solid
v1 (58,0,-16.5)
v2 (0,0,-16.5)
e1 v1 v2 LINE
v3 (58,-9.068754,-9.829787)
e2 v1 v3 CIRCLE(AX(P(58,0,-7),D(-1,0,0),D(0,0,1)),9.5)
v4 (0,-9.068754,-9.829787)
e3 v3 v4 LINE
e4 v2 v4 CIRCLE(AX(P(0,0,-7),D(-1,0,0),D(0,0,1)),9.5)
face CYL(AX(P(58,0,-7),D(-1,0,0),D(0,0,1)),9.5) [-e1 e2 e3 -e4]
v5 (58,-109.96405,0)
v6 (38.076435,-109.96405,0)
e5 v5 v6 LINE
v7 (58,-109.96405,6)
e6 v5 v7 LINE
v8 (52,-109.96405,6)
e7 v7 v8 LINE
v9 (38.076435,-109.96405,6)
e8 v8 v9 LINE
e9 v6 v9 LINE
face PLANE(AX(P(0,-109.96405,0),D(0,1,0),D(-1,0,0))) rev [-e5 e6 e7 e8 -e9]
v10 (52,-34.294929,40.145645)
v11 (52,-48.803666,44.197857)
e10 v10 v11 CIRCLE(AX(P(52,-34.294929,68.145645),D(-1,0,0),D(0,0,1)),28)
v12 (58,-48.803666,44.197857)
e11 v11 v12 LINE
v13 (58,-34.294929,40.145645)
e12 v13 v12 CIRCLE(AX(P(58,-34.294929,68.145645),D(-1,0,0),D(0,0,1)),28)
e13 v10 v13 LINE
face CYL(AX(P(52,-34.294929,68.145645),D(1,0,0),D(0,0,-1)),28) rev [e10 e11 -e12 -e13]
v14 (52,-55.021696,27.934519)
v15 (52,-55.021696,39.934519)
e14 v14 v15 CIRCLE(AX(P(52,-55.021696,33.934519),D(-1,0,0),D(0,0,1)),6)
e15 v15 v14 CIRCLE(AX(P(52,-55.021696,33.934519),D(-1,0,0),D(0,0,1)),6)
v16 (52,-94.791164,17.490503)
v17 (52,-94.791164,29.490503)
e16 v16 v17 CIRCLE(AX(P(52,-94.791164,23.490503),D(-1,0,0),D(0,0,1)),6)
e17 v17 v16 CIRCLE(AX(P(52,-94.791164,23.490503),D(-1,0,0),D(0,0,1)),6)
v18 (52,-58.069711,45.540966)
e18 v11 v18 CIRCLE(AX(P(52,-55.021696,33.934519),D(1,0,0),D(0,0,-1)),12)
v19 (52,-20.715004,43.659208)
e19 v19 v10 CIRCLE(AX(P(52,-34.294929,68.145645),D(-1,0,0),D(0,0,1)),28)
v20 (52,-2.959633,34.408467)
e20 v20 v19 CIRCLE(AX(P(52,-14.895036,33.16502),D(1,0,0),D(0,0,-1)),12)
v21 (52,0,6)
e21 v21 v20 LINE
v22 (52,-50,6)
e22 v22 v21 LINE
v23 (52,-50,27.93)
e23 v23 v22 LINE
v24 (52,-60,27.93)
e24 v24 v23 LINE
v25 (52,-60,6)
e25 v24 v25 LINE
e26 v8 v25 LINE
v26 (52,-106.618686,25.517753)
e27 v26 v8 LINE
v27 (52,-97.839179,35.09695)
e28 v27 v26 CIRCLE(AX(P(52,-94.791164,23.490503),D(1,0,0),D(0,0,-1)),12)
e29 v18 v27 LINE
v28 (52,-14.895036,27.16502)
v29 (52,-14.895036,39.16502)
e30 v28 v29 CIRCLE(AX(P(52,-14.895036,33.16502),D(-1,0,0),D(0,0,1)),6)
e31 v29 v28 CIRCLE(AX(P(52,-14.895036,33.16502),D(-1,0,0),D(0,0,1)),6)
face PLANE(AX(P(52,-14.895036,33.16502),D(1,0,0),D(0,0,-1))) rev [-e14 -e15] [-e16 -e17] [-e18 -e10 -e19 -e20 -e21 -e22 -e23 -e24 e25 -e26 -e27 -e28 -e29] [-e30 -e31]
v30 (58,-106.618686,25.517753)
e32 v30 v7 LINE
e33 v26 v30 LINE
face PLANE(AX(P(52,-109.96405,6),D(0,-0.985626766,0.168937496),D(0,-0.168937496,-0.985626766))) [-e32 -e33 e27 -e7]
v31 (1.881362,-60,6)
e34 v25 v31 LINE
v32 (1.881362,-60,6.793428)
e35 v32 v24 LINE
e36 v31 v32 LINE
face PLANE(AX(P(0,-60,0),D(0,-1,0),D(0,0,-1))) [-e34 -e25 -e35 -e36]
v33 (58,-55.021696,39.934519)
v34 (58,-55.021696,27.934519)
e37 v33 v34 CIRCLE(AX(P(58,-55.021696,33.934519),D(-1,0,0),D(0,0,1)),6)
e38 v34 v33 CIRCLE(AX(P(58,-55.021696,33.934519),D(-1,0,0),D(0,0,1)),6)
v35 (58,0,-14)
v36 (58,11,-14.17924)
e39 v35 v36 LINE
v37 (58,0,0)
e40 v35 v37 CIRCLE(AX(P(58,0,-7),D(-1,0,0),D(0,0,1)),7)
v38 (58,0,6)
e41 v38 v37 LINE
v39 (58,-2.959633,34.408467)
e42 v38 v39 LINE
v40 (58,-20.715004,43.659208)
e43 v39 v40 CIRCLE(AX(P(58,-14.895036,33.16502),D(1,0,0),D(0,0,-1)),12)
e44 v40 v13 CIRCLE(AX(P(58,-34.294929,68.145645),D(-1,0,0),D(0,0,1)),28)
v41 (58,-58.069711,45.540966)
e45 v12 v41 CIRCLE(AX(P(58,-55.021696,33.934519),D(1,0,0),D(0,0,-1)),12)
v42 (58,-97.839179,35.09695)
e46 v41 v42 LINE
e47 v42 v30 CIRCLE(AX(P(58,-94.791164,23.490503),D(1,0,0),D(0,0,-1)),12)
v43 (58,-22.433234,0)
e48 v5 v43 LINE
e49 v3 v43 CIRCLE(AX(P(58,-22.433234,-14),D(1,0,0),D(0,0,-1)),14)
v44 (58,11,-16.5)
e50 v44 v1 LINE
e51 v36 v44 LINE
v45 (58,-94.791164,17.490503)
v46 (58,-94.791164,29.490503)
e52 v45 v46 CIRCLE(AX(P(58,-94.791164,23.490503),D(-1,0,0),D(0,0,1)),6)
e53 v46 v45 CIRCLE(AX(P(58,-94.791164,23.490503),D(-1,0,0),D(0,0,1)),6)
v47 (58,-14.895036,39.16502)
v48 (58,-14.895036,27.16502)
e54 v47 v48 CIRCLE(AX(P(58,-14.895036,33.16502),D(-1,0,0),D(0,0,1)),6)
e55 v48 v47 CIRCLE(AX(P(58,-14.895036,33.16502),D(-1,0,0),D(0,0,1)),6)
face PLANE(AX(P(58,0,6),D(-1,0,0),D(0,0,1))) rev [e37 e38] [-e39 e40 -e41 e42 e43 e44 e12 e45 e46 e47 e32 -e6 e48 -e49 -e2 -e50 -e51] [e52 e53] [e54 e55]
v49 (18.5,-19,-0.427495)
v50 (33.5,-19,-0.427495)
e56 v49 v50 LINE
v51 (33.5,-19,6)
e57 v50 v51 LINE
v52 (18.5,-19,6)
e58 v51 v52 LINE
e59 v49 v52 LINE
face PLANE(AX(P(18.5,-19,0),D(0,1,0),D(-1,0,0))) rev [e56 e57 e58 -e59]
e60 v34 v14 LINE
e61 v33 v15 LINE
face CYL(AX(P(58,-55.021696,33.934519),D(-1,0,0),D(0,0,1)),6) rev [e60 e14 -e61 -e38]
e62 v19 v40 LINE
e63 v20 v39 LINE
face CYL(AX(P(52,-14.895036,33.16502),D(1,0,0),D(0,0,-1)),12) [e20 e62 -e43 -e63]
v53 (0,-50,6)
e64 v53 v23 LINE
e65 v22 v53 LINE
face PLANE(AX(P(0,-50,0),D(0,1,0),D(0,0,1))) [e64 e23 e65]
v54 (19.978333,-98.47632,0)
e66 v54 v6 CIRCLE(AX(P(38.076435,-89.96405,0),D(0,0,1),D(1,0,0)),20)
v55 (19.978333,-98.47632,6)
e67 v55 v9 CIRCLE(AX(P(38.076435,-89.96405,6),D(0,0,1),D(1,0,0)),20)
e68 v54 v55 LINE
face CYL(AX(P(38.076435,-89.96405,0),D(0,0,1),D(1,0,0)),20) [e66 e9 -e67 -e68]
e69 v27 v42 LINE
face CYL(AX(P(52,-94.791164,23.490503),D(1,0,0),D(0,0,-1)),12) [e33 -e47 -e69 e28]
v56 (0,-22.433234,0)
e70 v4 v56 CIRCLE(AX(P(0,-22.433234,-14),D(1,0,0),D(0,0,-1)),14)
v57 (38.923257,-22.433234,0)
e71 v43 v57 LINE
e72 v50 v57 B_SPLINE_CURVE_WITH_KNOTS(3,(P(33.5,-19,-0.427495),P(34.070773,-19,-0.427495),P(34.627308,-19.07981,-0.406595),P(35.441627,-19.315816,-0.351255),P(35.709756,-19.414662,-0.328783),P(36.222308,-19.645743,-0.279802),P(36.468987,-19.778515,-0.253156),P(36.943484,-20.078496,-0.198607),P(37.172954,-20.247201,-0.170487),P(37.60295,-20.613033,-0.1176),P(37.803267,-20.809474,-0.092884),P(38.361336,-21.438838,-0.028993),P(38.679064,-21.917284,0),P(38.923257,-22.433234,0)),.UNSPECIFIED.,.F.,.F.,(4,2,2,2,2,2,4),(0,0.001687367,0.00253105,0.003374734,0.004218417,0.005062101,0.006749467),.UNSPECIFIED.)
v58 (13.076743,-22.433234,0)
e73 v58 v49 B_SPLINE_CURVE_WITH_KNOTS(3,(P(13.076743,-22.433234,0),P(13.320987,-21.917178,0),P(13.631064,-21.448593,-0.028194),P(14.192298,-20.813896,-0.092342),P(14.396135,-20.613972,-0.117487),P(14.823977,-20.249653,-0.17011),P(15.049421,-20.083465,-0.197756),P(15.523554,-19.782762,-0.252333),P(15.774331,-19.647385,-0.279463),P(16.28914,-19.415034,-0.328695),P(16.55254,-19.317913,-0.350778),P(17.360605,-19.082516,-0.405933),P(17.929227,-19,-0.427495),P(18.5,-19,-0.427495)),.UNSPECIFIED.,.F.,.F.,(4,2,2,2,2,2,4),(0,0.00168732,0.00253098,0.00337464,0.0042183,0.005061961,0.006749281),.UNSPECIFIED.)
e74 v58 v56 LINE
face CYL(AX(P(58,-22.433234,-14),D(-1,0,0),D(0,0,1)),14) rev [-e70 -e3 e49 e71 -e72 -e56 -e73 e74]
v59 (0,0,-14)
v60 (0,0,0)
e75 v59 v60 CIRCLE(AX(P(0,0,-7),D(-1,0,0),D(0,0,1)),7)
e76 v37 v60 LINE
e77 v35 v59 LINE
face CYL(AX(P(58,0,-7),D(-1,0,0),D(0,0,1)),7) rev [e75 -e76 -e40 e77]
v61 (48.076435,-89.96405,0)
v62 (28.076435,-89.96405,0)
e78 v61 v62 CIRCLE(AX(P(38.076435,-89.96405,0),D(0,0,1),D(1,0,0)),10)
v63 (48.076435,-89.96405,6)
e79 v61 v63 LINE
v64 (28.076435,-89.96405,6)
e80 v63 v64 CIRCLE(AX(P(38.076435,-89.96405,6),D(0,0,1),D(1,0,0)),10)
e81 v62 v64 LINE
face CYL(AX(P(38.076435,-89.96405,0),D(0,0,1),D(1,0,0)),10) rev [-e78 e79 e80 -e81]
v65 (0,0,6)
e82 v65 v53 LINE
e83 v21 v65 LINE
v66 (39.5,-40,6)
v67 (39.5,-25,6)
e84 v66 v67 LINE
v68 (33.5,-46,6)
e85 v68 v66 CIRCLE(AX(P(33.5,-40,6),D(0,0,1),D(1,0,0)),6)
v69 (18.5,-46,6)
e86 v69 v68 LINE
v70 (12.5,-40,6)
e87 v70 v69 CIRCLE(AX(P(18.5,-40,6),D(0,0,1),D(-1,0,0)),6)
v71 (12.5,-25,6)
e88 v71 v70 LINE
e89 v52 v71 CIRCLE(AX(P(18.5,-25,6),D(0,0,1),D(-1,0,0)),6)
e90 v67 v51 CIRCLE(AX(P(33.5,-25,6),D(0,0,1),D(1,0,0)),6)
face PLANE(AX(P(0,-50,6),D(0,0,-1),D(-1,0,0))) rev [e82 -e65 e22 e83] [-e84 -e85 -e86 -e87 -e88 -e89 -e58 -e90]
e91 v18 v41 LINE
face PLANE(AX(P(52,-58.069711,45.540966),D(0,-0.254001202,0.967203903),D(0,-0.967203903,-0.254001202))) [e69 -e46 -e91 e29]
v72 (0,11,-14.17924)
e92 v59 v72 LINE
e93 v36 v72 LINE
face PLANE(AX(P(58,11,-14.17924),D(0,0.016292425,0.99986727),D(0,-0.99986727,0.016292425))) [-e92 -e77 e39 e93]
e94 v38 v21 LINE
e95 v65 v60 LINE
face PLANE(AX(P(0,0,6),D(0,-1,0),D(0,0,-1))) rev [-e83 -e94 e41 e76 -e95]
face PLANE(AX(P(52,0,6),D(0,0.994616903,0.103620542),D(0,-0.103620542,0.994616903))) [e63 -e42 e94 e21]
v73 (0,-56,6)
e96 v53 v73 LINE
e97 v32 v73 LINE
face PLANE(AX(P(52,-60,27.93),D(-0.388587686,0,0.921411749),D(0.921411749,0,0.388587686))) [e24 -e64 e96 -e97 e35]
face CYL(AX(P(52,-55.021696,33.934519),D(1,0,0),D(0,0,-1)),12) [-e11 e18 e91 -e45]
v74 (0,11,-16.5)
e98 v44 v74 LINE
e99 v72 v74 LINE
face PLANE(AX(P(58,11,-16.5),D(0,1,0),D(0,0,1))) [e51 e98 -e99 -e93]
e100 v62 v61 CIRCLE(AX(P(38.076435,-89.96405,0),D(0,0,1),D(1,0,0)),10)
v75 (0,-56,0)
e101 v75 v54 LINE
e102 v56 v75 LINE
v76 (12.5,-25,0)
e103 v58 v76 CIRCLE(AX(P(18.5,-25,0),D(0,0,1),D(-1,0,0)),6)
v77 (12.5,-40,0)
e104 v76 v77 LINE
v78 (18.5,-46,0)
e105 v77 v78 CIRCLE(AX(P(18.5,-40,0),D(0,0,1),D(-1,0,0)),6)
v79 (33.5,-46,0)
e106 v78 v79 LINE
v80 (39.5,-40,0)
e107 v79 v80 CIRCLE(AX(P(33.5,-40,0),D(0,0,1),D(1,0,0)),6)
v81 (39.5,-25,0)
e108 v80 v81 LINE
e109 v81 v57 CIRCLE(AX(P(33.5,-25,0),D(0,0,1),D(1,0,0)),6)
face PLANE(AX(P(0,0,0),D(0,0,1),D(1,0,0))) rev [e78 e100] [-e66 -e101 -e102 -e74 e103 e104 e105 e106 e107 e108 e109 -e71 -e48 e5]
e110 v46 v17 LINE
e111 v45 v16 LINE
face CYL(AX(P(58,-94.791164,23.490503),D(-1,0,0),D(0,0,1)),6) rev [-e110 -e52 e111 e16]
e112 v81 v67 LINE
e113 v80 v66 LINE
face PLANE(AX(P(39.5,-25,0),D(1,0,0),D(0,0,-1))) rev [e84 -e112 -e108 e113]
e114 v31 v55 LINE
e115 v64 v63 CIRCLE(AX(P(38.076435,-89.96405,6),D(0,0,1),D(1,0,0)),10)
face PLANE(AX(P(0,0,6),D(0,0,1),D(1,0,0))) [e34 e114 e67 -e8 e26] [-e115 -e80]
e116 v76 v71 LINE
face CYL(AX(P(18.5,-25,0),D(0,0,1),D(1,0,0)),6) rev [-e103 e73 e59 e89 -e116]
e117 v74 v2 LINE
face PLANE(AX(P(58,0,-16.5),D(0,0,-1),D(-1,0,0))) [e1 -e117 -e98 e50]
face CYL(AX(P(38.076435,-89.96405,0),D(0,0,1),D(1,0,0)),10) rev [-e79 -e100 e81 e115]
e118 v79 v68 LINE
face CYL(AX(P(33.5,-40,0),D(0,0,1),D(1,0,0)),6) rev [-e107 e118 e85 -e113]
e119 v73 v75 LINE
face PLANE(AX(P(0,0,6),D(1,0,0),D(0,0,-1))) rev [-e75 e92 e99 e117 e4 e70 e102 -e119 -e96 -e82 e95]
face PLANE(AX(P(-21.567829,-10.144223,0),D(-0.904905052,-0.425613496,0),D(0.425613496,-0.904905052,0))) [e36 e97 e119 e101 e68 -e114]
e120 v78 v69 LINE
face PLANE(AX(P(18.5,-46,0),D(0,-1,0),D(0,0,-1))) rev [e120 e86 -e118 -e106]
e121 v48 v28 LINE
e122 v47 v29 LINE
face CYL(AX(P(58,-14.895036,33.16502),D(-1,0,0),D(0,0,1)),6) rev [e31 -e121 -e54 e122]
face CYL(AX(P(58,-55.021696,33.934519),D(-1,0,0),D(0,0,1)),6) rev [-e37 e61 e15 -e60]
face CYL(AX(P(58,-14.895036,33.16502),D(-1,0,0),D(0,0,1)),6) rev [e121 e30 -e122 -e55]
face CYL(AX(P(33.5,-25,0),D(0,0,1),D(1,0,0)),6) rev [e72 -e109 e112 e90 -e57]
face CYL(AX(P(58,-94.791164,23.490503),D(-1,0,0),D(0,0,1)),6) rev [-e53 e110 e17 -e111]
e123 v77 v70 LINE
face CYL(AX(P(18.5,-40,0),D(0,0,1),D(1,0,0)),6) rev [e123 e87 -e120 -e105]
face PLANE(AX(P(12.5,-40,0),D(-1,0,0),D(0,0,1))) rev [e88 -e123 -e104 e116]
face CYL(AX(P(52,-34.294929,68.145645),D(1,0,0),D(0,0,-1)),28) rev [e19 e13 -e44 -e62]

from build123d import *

# Parameters (mm, degrees)
BASE_PLATE_SKETCH_W      = 58
BASE_PLATE_SKETCH_H      = 56
BASE_PLATE_DEPTH         = 6
CHANNEL_WALL_DEPTH       = 58
CHANNEL_GROOVE_CUT_DEPTH = 58
GROOVE_LIP_DEPTH         = 58
SIDE_ARM_DEPTH           = 6
LUG_PLATE_DEPTH          = 6
UPPER_HOLE_SKETCH_R      = 6
UPPER_HOLE_DEPTH         = 6
MIDDLE_HOLE_SKETCH_R     = 10
MIDDLE_HOLE_DEPTH        = 6
GUSSET_DEPTH             = 60
GUSSET_TRIM_CUT_A_DEPTH  = 50
GUSSET_TRIM_CUT_B_DEPTH  = 50
ARM_PROFILE_CUT_DEPTH    = 6
LOWER_HOLE_DEPTH         = 6


with BuildPart() as part:
    # Base Plate Sketch → Base Plate (new body)
    with BuildSketch(Plane.XY):
        with Locations((29, -28)):
            Rectangle(BASE_PLATE_SKETCH_W, BASE_PLATE_SKETCH_H)
    extrude(amount=BASE_PLATE_DEPTH)

    # Channel Wall Sketch → Channel Wall (add)
    with BuildSketch(Plane.ZY):
        with BuildLine():
            Line((0, 0), (-7, 0))
            Line((-7, 0), (-16.5, 0))
            ThreePointArc((-16.5, 0), (-14.652874582, -5.628810766), (-9.829787234, -9.068754281))
            ThreePointArc((-9.829787234, -9.068754281), (-2.722079564, -14.138144724), (0, -22.433234274))
            Line((0, -22.433234274), (0, 0))
        make_face()
    extrude(amount=-CHANNEL_WALL_DEPTH)

    # Channel Groove Sketch → Channel Groove Cut (cut)
    with BuildSketch(Plane.ZY):
        with BuildLine():
            Line((-14, 0), (0, 0))
            ThreePointArc((0, 0), (-7, -7), (-14, 0))
        make_face()
    extrude(amount=-CHANNEL_GROOVE_CUT_DEPTH, mode=Mode.SUBTRACT)

    # Groove Lip Sketch → Groove Lip (add)
    with BuildSketch(Plane.ZY):
        Polygon((-16.5, 0), (-16.5, 11), (-14.179240466, 11), (-14, 0), align=None)
    extrude(amount=-GROOVE_LIP_DEPTH)

    # Side Arm Sketch → Side Arm (add)
    with BuildSketch(Plane.XY.offset(6)):
        with BuildLine():
            Line((58, -109.964049753), (58, -56))
            Line((58, -56), (0, -56))
            Line((0, -56), (19.97833348, -98.476319664))
            ThreePointArc((19.97833348, -98.476319664), (27.35835162, -106.849626412), (38.076434513, -109.964049753))
            Line((38.076434513, -109.964049753), (58, -109.964049753))
        make_face()
    extrude(amount=-SIDE_ARM_DEPTH)

    # Lug Plate Sketch → Lug Plate (add)
    with BuildSketch(Plane(origin=(58, 0, 0), x_dir=(0, 0, -1), z_dir=(1, 0, 0))):
        with BuildLine():
            Line((-6, -109.964049753), (-25.517753411, -106.618685655))
            ThreePointArc((-25.517753411, -106.618685655), (-31.598484509, -103.637669036), (-35.096950284, -97.83917889))
            Line((-35.096950284, -97.83917889), (-45.54096595, -58.069710813))
            ThreePointArc((-45.54096595, -58.069710813), (-45.810409179, -53.300291354), (-44.197856883, -48.803666316))
            ThreePointArc((-44.197856883, -48.803666316), (-40.150792049, -34.831779802), (-43.659207606, -20.715003724))
            ThreePointArc((-43.659207606, -20.715003724), (-43.807215073, -9.350336516), (-34.408466657, -2.959632707))
            Line((-34.408466657, -2.959632707), (-6, 0))
            Line((-6, 0), (-6, -109.964049753))
        make_face()
    extrude(amount=-LUG_PLATE_DEPTH)

    # Upper Hole Sketch → Upper Hole (cut)
    with BuildSketch(Plane.ZY.offset(-52)):
        with Locations((33.165020152, -14.89503554)):
            Circle(UPPER_HOLE_SKETCH_R)
        with Locations((33.934519119, -55.021696385)):
            Circle(UPPER_HOLE_SKETCH_R)
        with Locations((23.490503453, -94.791164461)):
            Circle(UPPER_HOLE_SKETCH_R)
    extrude(amount=-UPPER_HOLE_DEPTH, mode=Mode.SUBTRACT)

    # Middle Hole Sketch → Middle Hole (cut)
    with BuildSketch(Plane.XY.offset(6)):
        with Locations((38.076434513, -89.964049753)):
            Circle(MIDDLE_HOLE_SKETCH_R)
    extrude(amount=-MIDDLE_HOLE_DEPTH, mode=Mode.SUBTRACT)

    # Gusset Sketch → Gusset (add)
    with BuildSketch(Plane(origin=(0, 0, 0), x_dir=(1, 0, 0), z_dir=(0, 1, 0))):
        Polygon((52, -6), (52, -27.93), (0, -6), align=None)
    extrude(amount=-GUSSET_DEPTH)

    # Gusset Trim Sketch A → Gusset Trim Cut A (cut)
    with BuildSketch(Plane(origin=(0, 0, 0), x_dir=(1, 0, 0), z_dir=(0, 1, 0))):
        Polygon((0, -6), (52, -6), (52, -27.93), align=None)
    extrude(amount=-GUSSET_TRIM_CUT_A_DEPTH, mode=Mode.SUBTRACT)

    # Gusset Trim Sketch B → Gusset Trim Cut B (cut)
    with BuildSketch(Plane(origin=(0, 0, 6), x_dir=(-1, 0, 0), z_dir=(0, 0, -1))):
        Polygon((-1.881362005, -60), (0, -56), (0, -60), align=None)
    extrude(amount=-GUSSET_TRIM_CUT_B_DEPTH, mode=Mode.SUBTRACT)

    # Arm Profile Cut Sketch → Arm Profile Cut (cut)
    with BuildSketch(Plane.XY.offset(6)):
        with BuildLine():
            Line((18.5, -46), (33.5, -46))
            ThreePointArc((33.5, -46), (37.742640687, -44.242640687), (39.5, -40))
            Line((39.5, -40), (39.5, -25))
            ThreePointArc((39.5, -25), (37.742640687, -20.757359313), (33.5, -19))
            Line((33.5, -19), (18.5, -19))
            ThreePointArc((18.5, -19), (14.257359313, -20.757359313), (12.5, -25))
            Line((12.5, -25), (12.5, -40))
            ThreePointArc((12.5, -40), (14.257359313, -44.242640687), (18.5, -46))
        make_face()
    extrude(amount=-ARM_PROFILE_CUT_DEPTH, mode=Mode.SUBTRACT)

    # Lower Hole Sketch → Lower Hole (cut)
    with BuildSketch(Plane.XY):
        with BuildLine():
            Line((13.076743256, -22.433234274), (38.923256744, -22.433234274))
            ThreePointArc((38.923256744, -22.433234274), (36.709315008, -19.930453948), (33.5, -19))
            Line((33.5, -19), (18.5, -19))
            ThreePointArc((18.5, -19), (15.290684992, -19.930453948), (13.076743256, -22.433234274))
        make_face()
    extrude(amount=-LOWER_HOLE_DEPTH, mode=Mode.SUBTRACT)


solid = part.part
